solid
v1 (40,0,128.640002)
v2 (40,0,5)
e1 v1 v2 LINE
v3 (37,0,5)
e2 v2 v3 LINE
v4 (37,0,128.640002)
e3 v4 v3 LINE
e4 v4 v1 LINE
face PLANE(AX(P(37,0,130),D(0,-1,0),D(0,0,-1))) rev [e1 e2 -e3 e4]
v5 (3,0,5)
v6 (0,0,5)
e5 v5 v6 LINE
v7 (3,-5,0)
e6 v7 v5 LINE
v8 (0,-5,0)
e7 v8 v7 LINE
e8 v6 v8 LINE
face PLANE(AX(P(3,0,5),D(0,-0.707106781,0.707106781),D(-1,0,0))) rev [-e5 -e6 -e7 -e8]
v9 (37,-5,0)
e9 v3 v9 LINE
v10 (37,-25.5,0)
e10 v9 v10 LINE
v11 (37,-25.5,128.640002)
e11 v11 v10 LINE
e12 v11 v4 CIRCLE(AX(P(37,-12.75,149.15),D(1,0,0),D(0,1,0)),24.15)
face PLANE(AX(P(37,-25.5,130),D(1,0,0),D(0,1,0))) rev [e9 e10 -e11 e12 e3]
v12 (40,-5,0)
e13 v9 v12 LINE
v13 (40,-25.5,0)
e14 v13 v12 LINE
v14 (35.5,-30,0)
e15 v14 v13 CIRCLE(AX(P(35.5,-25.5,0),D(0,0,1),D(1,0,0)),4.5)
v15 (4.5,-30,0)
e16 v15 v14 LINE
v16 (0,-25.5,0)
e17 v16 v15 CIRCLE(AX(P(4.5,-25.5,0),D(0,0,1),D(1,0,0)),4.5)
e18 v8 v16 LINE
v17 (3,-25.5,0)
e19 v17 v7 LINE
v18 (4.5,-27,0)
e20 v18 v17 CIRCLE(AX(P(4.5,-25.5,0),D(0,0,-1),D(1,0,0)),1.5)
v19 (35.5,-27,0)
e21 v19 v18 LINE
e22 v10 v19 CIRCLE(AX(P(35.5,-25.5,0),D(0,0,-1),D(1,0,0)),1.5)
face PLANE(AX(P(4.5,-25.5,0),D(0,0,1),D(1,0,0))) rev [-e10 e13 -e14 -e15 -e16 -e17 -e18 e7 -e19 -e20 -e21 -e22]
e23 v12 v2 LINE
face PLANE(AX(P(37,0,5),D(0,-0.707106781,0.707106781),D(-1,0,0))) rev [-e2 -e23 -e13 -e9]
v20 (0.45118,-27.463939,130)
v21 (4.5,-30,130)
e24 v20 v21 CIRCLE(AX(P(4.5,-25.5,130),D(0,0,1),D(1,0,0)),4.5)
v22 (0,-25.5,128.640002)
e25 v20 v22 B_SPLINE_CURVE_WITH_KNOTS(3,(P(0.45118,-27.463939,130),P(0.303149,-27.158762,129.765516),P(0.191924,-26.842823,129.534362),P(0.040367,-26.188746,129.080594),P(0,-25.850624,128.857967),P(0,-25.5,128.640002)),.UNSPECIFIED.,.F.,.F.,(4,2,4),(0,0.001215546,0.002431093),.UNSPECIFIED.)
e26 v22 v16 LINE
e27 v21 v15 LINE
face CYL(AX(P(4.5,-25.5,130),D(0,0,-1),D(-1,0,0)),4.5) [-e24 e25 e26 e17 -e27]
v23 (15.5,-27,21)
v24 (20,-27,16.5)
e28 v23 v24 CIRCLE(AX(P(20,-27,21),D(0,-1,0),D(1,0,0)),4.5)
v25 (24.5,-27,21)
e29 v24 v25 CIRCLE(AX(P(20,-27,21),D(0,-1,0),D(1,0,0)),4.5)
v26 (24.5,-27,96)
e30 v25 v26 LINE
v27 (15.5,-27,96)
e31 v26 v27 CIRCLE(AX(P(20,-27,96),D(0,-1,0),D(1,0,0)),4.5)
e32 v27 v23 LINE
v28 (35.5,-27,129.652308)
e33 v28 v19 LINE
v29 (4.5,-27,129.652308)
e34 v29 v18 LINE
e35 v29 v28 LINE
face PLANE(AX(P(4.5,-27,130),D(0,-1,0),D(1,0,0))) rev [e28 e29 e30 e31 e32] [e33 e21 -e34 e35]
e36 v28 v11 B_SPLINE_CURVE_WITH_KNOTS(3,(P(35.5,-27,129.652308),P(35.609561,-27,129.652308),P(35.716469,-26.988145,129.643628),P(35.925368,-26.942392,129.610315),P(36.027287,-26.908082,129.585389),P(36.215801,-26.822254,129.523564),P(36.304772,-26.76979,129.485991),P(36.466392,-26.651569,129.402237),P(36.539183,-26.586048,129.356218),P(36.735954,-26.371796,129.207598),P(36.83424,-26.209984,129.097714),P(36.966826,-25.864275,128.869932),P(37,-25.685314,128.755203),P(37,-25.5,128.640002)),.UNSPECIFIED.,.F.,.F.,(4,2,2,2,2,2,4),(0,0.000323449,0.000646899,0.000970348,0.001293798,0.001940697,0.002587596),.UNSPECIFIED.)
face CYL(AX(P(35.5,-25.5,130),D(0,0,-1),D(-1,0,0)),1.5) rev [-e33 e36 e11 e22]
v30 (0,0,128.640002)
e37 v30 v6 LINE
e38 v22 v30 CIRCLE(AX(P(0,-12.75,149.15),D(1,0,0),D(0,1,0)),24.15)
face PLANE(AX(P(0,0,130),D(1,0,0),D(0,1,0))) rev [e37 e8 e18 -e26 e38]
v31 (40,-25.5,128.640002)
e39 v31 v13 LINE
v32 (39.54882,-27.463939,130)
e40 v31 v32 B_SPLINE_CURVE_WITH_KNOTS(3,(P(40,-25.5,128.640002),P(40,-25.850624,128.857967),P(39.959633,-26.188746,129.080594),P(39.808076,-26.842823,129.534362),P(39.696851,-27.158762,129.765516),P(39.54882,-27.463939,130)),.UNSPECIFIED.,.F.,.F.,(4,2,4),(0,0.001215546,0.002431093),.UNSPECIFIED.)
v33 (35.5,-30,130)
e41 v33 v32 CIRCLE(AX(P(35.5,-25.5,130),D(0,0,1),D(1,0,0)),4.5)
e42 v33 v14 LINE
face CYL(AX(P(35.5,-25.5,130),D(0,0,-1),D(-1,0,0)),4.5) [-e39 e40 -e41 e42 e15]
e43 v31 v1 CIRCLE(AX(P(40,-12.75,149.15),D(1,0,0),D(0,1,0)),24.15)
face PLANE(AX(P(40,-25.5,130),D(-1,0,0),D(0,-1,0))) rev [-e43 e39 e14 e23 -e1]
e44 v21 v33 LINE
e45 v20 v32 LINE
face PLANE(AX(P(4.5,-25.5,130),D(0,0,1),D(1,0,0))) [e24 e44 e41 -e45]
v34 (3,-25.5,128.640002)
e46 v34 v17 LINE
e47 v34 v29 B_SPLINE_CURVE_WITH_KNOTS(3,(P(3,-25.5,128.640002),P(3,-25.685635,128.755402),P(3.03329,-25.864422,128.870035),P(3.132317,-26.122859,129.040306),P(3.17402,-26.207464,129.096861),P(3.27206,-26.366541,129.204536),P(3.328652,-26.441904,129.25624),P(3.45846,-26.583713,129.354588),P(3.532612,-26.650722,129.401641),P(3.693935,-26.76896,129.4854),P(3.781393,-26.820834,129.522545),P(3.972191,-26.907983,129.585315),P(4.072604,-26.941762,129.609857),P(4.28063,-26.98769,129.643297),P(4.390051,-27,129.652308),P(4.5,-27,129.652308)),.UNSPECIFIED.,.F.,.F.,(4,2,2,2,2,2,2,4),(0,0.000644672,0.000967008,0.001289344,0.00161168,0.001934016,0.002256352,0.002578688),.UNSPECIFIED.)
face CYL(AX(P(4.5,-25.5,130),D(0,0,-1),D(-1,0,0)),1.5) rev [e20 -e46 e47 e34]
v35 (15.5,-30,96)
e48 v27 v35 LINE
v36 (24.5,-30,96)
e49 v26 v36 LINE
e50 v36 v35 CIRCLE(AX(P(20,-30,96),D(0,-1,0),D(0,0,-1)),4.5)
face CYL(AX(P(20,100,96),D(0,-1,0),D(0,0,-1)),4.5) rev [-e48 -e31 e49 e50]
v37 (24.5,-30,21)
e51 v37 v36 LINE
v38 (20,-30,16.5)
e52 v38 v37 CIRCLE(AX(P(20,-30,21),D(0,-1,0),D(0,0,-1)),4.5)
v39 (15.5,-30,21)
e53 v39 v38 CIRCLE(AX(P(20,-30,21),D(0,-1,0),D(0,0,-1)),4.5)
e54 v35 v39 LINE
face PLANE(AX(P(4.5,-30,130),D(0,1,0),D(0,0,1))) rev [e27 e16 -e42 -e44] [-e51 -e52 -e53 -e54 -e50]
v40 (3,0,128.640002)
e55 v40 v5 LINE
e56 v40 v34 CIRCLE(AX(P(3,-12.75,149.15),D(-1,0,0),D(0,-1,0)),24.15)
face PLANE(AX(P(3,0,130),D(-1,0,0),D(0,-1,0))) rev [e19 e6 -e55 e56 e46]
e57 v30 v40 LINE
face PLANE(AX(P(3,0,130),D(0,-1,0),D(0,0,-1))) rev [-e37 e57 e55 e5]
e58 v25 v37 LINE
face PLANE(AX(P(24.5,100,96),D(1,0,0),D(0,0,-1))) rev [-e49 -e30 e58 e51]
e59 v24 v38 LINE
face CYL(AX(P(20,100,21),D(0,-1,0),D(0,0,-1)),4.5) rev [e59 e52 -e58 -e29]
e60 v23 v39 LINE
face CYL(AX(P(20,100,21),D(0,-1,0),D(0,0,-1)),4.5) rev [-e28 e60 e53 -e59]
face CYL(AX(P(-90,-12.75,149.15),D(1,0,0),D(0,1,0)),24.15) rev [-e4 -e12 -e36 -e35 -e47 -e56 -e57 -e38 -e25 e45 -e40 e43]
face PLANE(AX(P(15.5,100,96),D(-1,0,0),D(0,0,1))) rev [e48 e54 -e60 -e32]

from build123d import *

# Parameters (mm, degrees)
BOSS_EXTRUDE1_DEPTH = 130
CHAMFER1_SIZE       = 5
SKETCH2_R           = 24.15
CUT_EXTRUDE1_DEPTH  = 130
CUT_EXTRUDE2_DEPTH  = 130


with BuildPart() as part:
    # Sketch1 → Boss-Extrude1 (new body)
    with BuildSketch(Plane.XY):
        with BuildLine():
            Line((0, 0), (0, -25.5))
            ThreePointArc((0, -25.5), (1.318019485, -28.681980515), (4.5, -30))
            Line((4.5, -30), (35.5, -30))
            ThreePointArc((35.5, -30), (38.681980515, -28.681980515), (40, -25.5))
            Line((40, -25.5), (40, 0))
            Line((40, 0), (37, 0))
            Line((37, 0), (37, -25.5))
            ThreePointArc((37, -25.5), (36.560660172, -26.560660172), (35.5, -27))
            Line((35.5, -27), (4.5, -27))
            ThreePointArc((4.5, -27), (3.439339828, -26.560660172), (3, -25.5))
            Line((3, -25.5), (3, 0))
            Line((3, 0), (0, 0))
        make_face()
    extrude(amount=BOSS_EXTRUDE1_DEPTH)

    # Chamfer1
    chamfer1_edges = [part.edges().sort_by_distance(p)[0] for p in [
        (38.5, 0, 0),
        (1.5, 0, 0),
    ]]
    chamfer(chamfer1_edges, length=CHAMFER1_SIZE)

    # Sketch2 → Cut-Extrude1 (cut)
    with BuildSketch(Plane(origin=(40, 0, 0), x_dir=(0, 0, -1), z_dir=(1, 0, 0))):
        with Locations((-149.15, -12.75)):
            Circle(SKETCH2_R)
    extrude(amount=-CUT_EXTRUDE1_DEPTH, mode=Mode.SUBTRACT)

    # Sketch3 → Cut-Extrude2 (cut)
    with BuildSketch(Plane.XZ.offset(30)):
        with BuildLine():
            Line((24.5, 96), (24.5, 21))
            ThreePointArc((24.5, 21), (20, 16.5), (15.5, 21))
            Line((15.5, 21), (15.5, 96))
            ThreePointArc((15.5, 96), (20, 100.5), (24.5, 96))
        make_face()
    extrude(amount=-CUT_EXTRUDE2_DEPTH, mode=Mode.SUBTRACT)


solid = part.part
